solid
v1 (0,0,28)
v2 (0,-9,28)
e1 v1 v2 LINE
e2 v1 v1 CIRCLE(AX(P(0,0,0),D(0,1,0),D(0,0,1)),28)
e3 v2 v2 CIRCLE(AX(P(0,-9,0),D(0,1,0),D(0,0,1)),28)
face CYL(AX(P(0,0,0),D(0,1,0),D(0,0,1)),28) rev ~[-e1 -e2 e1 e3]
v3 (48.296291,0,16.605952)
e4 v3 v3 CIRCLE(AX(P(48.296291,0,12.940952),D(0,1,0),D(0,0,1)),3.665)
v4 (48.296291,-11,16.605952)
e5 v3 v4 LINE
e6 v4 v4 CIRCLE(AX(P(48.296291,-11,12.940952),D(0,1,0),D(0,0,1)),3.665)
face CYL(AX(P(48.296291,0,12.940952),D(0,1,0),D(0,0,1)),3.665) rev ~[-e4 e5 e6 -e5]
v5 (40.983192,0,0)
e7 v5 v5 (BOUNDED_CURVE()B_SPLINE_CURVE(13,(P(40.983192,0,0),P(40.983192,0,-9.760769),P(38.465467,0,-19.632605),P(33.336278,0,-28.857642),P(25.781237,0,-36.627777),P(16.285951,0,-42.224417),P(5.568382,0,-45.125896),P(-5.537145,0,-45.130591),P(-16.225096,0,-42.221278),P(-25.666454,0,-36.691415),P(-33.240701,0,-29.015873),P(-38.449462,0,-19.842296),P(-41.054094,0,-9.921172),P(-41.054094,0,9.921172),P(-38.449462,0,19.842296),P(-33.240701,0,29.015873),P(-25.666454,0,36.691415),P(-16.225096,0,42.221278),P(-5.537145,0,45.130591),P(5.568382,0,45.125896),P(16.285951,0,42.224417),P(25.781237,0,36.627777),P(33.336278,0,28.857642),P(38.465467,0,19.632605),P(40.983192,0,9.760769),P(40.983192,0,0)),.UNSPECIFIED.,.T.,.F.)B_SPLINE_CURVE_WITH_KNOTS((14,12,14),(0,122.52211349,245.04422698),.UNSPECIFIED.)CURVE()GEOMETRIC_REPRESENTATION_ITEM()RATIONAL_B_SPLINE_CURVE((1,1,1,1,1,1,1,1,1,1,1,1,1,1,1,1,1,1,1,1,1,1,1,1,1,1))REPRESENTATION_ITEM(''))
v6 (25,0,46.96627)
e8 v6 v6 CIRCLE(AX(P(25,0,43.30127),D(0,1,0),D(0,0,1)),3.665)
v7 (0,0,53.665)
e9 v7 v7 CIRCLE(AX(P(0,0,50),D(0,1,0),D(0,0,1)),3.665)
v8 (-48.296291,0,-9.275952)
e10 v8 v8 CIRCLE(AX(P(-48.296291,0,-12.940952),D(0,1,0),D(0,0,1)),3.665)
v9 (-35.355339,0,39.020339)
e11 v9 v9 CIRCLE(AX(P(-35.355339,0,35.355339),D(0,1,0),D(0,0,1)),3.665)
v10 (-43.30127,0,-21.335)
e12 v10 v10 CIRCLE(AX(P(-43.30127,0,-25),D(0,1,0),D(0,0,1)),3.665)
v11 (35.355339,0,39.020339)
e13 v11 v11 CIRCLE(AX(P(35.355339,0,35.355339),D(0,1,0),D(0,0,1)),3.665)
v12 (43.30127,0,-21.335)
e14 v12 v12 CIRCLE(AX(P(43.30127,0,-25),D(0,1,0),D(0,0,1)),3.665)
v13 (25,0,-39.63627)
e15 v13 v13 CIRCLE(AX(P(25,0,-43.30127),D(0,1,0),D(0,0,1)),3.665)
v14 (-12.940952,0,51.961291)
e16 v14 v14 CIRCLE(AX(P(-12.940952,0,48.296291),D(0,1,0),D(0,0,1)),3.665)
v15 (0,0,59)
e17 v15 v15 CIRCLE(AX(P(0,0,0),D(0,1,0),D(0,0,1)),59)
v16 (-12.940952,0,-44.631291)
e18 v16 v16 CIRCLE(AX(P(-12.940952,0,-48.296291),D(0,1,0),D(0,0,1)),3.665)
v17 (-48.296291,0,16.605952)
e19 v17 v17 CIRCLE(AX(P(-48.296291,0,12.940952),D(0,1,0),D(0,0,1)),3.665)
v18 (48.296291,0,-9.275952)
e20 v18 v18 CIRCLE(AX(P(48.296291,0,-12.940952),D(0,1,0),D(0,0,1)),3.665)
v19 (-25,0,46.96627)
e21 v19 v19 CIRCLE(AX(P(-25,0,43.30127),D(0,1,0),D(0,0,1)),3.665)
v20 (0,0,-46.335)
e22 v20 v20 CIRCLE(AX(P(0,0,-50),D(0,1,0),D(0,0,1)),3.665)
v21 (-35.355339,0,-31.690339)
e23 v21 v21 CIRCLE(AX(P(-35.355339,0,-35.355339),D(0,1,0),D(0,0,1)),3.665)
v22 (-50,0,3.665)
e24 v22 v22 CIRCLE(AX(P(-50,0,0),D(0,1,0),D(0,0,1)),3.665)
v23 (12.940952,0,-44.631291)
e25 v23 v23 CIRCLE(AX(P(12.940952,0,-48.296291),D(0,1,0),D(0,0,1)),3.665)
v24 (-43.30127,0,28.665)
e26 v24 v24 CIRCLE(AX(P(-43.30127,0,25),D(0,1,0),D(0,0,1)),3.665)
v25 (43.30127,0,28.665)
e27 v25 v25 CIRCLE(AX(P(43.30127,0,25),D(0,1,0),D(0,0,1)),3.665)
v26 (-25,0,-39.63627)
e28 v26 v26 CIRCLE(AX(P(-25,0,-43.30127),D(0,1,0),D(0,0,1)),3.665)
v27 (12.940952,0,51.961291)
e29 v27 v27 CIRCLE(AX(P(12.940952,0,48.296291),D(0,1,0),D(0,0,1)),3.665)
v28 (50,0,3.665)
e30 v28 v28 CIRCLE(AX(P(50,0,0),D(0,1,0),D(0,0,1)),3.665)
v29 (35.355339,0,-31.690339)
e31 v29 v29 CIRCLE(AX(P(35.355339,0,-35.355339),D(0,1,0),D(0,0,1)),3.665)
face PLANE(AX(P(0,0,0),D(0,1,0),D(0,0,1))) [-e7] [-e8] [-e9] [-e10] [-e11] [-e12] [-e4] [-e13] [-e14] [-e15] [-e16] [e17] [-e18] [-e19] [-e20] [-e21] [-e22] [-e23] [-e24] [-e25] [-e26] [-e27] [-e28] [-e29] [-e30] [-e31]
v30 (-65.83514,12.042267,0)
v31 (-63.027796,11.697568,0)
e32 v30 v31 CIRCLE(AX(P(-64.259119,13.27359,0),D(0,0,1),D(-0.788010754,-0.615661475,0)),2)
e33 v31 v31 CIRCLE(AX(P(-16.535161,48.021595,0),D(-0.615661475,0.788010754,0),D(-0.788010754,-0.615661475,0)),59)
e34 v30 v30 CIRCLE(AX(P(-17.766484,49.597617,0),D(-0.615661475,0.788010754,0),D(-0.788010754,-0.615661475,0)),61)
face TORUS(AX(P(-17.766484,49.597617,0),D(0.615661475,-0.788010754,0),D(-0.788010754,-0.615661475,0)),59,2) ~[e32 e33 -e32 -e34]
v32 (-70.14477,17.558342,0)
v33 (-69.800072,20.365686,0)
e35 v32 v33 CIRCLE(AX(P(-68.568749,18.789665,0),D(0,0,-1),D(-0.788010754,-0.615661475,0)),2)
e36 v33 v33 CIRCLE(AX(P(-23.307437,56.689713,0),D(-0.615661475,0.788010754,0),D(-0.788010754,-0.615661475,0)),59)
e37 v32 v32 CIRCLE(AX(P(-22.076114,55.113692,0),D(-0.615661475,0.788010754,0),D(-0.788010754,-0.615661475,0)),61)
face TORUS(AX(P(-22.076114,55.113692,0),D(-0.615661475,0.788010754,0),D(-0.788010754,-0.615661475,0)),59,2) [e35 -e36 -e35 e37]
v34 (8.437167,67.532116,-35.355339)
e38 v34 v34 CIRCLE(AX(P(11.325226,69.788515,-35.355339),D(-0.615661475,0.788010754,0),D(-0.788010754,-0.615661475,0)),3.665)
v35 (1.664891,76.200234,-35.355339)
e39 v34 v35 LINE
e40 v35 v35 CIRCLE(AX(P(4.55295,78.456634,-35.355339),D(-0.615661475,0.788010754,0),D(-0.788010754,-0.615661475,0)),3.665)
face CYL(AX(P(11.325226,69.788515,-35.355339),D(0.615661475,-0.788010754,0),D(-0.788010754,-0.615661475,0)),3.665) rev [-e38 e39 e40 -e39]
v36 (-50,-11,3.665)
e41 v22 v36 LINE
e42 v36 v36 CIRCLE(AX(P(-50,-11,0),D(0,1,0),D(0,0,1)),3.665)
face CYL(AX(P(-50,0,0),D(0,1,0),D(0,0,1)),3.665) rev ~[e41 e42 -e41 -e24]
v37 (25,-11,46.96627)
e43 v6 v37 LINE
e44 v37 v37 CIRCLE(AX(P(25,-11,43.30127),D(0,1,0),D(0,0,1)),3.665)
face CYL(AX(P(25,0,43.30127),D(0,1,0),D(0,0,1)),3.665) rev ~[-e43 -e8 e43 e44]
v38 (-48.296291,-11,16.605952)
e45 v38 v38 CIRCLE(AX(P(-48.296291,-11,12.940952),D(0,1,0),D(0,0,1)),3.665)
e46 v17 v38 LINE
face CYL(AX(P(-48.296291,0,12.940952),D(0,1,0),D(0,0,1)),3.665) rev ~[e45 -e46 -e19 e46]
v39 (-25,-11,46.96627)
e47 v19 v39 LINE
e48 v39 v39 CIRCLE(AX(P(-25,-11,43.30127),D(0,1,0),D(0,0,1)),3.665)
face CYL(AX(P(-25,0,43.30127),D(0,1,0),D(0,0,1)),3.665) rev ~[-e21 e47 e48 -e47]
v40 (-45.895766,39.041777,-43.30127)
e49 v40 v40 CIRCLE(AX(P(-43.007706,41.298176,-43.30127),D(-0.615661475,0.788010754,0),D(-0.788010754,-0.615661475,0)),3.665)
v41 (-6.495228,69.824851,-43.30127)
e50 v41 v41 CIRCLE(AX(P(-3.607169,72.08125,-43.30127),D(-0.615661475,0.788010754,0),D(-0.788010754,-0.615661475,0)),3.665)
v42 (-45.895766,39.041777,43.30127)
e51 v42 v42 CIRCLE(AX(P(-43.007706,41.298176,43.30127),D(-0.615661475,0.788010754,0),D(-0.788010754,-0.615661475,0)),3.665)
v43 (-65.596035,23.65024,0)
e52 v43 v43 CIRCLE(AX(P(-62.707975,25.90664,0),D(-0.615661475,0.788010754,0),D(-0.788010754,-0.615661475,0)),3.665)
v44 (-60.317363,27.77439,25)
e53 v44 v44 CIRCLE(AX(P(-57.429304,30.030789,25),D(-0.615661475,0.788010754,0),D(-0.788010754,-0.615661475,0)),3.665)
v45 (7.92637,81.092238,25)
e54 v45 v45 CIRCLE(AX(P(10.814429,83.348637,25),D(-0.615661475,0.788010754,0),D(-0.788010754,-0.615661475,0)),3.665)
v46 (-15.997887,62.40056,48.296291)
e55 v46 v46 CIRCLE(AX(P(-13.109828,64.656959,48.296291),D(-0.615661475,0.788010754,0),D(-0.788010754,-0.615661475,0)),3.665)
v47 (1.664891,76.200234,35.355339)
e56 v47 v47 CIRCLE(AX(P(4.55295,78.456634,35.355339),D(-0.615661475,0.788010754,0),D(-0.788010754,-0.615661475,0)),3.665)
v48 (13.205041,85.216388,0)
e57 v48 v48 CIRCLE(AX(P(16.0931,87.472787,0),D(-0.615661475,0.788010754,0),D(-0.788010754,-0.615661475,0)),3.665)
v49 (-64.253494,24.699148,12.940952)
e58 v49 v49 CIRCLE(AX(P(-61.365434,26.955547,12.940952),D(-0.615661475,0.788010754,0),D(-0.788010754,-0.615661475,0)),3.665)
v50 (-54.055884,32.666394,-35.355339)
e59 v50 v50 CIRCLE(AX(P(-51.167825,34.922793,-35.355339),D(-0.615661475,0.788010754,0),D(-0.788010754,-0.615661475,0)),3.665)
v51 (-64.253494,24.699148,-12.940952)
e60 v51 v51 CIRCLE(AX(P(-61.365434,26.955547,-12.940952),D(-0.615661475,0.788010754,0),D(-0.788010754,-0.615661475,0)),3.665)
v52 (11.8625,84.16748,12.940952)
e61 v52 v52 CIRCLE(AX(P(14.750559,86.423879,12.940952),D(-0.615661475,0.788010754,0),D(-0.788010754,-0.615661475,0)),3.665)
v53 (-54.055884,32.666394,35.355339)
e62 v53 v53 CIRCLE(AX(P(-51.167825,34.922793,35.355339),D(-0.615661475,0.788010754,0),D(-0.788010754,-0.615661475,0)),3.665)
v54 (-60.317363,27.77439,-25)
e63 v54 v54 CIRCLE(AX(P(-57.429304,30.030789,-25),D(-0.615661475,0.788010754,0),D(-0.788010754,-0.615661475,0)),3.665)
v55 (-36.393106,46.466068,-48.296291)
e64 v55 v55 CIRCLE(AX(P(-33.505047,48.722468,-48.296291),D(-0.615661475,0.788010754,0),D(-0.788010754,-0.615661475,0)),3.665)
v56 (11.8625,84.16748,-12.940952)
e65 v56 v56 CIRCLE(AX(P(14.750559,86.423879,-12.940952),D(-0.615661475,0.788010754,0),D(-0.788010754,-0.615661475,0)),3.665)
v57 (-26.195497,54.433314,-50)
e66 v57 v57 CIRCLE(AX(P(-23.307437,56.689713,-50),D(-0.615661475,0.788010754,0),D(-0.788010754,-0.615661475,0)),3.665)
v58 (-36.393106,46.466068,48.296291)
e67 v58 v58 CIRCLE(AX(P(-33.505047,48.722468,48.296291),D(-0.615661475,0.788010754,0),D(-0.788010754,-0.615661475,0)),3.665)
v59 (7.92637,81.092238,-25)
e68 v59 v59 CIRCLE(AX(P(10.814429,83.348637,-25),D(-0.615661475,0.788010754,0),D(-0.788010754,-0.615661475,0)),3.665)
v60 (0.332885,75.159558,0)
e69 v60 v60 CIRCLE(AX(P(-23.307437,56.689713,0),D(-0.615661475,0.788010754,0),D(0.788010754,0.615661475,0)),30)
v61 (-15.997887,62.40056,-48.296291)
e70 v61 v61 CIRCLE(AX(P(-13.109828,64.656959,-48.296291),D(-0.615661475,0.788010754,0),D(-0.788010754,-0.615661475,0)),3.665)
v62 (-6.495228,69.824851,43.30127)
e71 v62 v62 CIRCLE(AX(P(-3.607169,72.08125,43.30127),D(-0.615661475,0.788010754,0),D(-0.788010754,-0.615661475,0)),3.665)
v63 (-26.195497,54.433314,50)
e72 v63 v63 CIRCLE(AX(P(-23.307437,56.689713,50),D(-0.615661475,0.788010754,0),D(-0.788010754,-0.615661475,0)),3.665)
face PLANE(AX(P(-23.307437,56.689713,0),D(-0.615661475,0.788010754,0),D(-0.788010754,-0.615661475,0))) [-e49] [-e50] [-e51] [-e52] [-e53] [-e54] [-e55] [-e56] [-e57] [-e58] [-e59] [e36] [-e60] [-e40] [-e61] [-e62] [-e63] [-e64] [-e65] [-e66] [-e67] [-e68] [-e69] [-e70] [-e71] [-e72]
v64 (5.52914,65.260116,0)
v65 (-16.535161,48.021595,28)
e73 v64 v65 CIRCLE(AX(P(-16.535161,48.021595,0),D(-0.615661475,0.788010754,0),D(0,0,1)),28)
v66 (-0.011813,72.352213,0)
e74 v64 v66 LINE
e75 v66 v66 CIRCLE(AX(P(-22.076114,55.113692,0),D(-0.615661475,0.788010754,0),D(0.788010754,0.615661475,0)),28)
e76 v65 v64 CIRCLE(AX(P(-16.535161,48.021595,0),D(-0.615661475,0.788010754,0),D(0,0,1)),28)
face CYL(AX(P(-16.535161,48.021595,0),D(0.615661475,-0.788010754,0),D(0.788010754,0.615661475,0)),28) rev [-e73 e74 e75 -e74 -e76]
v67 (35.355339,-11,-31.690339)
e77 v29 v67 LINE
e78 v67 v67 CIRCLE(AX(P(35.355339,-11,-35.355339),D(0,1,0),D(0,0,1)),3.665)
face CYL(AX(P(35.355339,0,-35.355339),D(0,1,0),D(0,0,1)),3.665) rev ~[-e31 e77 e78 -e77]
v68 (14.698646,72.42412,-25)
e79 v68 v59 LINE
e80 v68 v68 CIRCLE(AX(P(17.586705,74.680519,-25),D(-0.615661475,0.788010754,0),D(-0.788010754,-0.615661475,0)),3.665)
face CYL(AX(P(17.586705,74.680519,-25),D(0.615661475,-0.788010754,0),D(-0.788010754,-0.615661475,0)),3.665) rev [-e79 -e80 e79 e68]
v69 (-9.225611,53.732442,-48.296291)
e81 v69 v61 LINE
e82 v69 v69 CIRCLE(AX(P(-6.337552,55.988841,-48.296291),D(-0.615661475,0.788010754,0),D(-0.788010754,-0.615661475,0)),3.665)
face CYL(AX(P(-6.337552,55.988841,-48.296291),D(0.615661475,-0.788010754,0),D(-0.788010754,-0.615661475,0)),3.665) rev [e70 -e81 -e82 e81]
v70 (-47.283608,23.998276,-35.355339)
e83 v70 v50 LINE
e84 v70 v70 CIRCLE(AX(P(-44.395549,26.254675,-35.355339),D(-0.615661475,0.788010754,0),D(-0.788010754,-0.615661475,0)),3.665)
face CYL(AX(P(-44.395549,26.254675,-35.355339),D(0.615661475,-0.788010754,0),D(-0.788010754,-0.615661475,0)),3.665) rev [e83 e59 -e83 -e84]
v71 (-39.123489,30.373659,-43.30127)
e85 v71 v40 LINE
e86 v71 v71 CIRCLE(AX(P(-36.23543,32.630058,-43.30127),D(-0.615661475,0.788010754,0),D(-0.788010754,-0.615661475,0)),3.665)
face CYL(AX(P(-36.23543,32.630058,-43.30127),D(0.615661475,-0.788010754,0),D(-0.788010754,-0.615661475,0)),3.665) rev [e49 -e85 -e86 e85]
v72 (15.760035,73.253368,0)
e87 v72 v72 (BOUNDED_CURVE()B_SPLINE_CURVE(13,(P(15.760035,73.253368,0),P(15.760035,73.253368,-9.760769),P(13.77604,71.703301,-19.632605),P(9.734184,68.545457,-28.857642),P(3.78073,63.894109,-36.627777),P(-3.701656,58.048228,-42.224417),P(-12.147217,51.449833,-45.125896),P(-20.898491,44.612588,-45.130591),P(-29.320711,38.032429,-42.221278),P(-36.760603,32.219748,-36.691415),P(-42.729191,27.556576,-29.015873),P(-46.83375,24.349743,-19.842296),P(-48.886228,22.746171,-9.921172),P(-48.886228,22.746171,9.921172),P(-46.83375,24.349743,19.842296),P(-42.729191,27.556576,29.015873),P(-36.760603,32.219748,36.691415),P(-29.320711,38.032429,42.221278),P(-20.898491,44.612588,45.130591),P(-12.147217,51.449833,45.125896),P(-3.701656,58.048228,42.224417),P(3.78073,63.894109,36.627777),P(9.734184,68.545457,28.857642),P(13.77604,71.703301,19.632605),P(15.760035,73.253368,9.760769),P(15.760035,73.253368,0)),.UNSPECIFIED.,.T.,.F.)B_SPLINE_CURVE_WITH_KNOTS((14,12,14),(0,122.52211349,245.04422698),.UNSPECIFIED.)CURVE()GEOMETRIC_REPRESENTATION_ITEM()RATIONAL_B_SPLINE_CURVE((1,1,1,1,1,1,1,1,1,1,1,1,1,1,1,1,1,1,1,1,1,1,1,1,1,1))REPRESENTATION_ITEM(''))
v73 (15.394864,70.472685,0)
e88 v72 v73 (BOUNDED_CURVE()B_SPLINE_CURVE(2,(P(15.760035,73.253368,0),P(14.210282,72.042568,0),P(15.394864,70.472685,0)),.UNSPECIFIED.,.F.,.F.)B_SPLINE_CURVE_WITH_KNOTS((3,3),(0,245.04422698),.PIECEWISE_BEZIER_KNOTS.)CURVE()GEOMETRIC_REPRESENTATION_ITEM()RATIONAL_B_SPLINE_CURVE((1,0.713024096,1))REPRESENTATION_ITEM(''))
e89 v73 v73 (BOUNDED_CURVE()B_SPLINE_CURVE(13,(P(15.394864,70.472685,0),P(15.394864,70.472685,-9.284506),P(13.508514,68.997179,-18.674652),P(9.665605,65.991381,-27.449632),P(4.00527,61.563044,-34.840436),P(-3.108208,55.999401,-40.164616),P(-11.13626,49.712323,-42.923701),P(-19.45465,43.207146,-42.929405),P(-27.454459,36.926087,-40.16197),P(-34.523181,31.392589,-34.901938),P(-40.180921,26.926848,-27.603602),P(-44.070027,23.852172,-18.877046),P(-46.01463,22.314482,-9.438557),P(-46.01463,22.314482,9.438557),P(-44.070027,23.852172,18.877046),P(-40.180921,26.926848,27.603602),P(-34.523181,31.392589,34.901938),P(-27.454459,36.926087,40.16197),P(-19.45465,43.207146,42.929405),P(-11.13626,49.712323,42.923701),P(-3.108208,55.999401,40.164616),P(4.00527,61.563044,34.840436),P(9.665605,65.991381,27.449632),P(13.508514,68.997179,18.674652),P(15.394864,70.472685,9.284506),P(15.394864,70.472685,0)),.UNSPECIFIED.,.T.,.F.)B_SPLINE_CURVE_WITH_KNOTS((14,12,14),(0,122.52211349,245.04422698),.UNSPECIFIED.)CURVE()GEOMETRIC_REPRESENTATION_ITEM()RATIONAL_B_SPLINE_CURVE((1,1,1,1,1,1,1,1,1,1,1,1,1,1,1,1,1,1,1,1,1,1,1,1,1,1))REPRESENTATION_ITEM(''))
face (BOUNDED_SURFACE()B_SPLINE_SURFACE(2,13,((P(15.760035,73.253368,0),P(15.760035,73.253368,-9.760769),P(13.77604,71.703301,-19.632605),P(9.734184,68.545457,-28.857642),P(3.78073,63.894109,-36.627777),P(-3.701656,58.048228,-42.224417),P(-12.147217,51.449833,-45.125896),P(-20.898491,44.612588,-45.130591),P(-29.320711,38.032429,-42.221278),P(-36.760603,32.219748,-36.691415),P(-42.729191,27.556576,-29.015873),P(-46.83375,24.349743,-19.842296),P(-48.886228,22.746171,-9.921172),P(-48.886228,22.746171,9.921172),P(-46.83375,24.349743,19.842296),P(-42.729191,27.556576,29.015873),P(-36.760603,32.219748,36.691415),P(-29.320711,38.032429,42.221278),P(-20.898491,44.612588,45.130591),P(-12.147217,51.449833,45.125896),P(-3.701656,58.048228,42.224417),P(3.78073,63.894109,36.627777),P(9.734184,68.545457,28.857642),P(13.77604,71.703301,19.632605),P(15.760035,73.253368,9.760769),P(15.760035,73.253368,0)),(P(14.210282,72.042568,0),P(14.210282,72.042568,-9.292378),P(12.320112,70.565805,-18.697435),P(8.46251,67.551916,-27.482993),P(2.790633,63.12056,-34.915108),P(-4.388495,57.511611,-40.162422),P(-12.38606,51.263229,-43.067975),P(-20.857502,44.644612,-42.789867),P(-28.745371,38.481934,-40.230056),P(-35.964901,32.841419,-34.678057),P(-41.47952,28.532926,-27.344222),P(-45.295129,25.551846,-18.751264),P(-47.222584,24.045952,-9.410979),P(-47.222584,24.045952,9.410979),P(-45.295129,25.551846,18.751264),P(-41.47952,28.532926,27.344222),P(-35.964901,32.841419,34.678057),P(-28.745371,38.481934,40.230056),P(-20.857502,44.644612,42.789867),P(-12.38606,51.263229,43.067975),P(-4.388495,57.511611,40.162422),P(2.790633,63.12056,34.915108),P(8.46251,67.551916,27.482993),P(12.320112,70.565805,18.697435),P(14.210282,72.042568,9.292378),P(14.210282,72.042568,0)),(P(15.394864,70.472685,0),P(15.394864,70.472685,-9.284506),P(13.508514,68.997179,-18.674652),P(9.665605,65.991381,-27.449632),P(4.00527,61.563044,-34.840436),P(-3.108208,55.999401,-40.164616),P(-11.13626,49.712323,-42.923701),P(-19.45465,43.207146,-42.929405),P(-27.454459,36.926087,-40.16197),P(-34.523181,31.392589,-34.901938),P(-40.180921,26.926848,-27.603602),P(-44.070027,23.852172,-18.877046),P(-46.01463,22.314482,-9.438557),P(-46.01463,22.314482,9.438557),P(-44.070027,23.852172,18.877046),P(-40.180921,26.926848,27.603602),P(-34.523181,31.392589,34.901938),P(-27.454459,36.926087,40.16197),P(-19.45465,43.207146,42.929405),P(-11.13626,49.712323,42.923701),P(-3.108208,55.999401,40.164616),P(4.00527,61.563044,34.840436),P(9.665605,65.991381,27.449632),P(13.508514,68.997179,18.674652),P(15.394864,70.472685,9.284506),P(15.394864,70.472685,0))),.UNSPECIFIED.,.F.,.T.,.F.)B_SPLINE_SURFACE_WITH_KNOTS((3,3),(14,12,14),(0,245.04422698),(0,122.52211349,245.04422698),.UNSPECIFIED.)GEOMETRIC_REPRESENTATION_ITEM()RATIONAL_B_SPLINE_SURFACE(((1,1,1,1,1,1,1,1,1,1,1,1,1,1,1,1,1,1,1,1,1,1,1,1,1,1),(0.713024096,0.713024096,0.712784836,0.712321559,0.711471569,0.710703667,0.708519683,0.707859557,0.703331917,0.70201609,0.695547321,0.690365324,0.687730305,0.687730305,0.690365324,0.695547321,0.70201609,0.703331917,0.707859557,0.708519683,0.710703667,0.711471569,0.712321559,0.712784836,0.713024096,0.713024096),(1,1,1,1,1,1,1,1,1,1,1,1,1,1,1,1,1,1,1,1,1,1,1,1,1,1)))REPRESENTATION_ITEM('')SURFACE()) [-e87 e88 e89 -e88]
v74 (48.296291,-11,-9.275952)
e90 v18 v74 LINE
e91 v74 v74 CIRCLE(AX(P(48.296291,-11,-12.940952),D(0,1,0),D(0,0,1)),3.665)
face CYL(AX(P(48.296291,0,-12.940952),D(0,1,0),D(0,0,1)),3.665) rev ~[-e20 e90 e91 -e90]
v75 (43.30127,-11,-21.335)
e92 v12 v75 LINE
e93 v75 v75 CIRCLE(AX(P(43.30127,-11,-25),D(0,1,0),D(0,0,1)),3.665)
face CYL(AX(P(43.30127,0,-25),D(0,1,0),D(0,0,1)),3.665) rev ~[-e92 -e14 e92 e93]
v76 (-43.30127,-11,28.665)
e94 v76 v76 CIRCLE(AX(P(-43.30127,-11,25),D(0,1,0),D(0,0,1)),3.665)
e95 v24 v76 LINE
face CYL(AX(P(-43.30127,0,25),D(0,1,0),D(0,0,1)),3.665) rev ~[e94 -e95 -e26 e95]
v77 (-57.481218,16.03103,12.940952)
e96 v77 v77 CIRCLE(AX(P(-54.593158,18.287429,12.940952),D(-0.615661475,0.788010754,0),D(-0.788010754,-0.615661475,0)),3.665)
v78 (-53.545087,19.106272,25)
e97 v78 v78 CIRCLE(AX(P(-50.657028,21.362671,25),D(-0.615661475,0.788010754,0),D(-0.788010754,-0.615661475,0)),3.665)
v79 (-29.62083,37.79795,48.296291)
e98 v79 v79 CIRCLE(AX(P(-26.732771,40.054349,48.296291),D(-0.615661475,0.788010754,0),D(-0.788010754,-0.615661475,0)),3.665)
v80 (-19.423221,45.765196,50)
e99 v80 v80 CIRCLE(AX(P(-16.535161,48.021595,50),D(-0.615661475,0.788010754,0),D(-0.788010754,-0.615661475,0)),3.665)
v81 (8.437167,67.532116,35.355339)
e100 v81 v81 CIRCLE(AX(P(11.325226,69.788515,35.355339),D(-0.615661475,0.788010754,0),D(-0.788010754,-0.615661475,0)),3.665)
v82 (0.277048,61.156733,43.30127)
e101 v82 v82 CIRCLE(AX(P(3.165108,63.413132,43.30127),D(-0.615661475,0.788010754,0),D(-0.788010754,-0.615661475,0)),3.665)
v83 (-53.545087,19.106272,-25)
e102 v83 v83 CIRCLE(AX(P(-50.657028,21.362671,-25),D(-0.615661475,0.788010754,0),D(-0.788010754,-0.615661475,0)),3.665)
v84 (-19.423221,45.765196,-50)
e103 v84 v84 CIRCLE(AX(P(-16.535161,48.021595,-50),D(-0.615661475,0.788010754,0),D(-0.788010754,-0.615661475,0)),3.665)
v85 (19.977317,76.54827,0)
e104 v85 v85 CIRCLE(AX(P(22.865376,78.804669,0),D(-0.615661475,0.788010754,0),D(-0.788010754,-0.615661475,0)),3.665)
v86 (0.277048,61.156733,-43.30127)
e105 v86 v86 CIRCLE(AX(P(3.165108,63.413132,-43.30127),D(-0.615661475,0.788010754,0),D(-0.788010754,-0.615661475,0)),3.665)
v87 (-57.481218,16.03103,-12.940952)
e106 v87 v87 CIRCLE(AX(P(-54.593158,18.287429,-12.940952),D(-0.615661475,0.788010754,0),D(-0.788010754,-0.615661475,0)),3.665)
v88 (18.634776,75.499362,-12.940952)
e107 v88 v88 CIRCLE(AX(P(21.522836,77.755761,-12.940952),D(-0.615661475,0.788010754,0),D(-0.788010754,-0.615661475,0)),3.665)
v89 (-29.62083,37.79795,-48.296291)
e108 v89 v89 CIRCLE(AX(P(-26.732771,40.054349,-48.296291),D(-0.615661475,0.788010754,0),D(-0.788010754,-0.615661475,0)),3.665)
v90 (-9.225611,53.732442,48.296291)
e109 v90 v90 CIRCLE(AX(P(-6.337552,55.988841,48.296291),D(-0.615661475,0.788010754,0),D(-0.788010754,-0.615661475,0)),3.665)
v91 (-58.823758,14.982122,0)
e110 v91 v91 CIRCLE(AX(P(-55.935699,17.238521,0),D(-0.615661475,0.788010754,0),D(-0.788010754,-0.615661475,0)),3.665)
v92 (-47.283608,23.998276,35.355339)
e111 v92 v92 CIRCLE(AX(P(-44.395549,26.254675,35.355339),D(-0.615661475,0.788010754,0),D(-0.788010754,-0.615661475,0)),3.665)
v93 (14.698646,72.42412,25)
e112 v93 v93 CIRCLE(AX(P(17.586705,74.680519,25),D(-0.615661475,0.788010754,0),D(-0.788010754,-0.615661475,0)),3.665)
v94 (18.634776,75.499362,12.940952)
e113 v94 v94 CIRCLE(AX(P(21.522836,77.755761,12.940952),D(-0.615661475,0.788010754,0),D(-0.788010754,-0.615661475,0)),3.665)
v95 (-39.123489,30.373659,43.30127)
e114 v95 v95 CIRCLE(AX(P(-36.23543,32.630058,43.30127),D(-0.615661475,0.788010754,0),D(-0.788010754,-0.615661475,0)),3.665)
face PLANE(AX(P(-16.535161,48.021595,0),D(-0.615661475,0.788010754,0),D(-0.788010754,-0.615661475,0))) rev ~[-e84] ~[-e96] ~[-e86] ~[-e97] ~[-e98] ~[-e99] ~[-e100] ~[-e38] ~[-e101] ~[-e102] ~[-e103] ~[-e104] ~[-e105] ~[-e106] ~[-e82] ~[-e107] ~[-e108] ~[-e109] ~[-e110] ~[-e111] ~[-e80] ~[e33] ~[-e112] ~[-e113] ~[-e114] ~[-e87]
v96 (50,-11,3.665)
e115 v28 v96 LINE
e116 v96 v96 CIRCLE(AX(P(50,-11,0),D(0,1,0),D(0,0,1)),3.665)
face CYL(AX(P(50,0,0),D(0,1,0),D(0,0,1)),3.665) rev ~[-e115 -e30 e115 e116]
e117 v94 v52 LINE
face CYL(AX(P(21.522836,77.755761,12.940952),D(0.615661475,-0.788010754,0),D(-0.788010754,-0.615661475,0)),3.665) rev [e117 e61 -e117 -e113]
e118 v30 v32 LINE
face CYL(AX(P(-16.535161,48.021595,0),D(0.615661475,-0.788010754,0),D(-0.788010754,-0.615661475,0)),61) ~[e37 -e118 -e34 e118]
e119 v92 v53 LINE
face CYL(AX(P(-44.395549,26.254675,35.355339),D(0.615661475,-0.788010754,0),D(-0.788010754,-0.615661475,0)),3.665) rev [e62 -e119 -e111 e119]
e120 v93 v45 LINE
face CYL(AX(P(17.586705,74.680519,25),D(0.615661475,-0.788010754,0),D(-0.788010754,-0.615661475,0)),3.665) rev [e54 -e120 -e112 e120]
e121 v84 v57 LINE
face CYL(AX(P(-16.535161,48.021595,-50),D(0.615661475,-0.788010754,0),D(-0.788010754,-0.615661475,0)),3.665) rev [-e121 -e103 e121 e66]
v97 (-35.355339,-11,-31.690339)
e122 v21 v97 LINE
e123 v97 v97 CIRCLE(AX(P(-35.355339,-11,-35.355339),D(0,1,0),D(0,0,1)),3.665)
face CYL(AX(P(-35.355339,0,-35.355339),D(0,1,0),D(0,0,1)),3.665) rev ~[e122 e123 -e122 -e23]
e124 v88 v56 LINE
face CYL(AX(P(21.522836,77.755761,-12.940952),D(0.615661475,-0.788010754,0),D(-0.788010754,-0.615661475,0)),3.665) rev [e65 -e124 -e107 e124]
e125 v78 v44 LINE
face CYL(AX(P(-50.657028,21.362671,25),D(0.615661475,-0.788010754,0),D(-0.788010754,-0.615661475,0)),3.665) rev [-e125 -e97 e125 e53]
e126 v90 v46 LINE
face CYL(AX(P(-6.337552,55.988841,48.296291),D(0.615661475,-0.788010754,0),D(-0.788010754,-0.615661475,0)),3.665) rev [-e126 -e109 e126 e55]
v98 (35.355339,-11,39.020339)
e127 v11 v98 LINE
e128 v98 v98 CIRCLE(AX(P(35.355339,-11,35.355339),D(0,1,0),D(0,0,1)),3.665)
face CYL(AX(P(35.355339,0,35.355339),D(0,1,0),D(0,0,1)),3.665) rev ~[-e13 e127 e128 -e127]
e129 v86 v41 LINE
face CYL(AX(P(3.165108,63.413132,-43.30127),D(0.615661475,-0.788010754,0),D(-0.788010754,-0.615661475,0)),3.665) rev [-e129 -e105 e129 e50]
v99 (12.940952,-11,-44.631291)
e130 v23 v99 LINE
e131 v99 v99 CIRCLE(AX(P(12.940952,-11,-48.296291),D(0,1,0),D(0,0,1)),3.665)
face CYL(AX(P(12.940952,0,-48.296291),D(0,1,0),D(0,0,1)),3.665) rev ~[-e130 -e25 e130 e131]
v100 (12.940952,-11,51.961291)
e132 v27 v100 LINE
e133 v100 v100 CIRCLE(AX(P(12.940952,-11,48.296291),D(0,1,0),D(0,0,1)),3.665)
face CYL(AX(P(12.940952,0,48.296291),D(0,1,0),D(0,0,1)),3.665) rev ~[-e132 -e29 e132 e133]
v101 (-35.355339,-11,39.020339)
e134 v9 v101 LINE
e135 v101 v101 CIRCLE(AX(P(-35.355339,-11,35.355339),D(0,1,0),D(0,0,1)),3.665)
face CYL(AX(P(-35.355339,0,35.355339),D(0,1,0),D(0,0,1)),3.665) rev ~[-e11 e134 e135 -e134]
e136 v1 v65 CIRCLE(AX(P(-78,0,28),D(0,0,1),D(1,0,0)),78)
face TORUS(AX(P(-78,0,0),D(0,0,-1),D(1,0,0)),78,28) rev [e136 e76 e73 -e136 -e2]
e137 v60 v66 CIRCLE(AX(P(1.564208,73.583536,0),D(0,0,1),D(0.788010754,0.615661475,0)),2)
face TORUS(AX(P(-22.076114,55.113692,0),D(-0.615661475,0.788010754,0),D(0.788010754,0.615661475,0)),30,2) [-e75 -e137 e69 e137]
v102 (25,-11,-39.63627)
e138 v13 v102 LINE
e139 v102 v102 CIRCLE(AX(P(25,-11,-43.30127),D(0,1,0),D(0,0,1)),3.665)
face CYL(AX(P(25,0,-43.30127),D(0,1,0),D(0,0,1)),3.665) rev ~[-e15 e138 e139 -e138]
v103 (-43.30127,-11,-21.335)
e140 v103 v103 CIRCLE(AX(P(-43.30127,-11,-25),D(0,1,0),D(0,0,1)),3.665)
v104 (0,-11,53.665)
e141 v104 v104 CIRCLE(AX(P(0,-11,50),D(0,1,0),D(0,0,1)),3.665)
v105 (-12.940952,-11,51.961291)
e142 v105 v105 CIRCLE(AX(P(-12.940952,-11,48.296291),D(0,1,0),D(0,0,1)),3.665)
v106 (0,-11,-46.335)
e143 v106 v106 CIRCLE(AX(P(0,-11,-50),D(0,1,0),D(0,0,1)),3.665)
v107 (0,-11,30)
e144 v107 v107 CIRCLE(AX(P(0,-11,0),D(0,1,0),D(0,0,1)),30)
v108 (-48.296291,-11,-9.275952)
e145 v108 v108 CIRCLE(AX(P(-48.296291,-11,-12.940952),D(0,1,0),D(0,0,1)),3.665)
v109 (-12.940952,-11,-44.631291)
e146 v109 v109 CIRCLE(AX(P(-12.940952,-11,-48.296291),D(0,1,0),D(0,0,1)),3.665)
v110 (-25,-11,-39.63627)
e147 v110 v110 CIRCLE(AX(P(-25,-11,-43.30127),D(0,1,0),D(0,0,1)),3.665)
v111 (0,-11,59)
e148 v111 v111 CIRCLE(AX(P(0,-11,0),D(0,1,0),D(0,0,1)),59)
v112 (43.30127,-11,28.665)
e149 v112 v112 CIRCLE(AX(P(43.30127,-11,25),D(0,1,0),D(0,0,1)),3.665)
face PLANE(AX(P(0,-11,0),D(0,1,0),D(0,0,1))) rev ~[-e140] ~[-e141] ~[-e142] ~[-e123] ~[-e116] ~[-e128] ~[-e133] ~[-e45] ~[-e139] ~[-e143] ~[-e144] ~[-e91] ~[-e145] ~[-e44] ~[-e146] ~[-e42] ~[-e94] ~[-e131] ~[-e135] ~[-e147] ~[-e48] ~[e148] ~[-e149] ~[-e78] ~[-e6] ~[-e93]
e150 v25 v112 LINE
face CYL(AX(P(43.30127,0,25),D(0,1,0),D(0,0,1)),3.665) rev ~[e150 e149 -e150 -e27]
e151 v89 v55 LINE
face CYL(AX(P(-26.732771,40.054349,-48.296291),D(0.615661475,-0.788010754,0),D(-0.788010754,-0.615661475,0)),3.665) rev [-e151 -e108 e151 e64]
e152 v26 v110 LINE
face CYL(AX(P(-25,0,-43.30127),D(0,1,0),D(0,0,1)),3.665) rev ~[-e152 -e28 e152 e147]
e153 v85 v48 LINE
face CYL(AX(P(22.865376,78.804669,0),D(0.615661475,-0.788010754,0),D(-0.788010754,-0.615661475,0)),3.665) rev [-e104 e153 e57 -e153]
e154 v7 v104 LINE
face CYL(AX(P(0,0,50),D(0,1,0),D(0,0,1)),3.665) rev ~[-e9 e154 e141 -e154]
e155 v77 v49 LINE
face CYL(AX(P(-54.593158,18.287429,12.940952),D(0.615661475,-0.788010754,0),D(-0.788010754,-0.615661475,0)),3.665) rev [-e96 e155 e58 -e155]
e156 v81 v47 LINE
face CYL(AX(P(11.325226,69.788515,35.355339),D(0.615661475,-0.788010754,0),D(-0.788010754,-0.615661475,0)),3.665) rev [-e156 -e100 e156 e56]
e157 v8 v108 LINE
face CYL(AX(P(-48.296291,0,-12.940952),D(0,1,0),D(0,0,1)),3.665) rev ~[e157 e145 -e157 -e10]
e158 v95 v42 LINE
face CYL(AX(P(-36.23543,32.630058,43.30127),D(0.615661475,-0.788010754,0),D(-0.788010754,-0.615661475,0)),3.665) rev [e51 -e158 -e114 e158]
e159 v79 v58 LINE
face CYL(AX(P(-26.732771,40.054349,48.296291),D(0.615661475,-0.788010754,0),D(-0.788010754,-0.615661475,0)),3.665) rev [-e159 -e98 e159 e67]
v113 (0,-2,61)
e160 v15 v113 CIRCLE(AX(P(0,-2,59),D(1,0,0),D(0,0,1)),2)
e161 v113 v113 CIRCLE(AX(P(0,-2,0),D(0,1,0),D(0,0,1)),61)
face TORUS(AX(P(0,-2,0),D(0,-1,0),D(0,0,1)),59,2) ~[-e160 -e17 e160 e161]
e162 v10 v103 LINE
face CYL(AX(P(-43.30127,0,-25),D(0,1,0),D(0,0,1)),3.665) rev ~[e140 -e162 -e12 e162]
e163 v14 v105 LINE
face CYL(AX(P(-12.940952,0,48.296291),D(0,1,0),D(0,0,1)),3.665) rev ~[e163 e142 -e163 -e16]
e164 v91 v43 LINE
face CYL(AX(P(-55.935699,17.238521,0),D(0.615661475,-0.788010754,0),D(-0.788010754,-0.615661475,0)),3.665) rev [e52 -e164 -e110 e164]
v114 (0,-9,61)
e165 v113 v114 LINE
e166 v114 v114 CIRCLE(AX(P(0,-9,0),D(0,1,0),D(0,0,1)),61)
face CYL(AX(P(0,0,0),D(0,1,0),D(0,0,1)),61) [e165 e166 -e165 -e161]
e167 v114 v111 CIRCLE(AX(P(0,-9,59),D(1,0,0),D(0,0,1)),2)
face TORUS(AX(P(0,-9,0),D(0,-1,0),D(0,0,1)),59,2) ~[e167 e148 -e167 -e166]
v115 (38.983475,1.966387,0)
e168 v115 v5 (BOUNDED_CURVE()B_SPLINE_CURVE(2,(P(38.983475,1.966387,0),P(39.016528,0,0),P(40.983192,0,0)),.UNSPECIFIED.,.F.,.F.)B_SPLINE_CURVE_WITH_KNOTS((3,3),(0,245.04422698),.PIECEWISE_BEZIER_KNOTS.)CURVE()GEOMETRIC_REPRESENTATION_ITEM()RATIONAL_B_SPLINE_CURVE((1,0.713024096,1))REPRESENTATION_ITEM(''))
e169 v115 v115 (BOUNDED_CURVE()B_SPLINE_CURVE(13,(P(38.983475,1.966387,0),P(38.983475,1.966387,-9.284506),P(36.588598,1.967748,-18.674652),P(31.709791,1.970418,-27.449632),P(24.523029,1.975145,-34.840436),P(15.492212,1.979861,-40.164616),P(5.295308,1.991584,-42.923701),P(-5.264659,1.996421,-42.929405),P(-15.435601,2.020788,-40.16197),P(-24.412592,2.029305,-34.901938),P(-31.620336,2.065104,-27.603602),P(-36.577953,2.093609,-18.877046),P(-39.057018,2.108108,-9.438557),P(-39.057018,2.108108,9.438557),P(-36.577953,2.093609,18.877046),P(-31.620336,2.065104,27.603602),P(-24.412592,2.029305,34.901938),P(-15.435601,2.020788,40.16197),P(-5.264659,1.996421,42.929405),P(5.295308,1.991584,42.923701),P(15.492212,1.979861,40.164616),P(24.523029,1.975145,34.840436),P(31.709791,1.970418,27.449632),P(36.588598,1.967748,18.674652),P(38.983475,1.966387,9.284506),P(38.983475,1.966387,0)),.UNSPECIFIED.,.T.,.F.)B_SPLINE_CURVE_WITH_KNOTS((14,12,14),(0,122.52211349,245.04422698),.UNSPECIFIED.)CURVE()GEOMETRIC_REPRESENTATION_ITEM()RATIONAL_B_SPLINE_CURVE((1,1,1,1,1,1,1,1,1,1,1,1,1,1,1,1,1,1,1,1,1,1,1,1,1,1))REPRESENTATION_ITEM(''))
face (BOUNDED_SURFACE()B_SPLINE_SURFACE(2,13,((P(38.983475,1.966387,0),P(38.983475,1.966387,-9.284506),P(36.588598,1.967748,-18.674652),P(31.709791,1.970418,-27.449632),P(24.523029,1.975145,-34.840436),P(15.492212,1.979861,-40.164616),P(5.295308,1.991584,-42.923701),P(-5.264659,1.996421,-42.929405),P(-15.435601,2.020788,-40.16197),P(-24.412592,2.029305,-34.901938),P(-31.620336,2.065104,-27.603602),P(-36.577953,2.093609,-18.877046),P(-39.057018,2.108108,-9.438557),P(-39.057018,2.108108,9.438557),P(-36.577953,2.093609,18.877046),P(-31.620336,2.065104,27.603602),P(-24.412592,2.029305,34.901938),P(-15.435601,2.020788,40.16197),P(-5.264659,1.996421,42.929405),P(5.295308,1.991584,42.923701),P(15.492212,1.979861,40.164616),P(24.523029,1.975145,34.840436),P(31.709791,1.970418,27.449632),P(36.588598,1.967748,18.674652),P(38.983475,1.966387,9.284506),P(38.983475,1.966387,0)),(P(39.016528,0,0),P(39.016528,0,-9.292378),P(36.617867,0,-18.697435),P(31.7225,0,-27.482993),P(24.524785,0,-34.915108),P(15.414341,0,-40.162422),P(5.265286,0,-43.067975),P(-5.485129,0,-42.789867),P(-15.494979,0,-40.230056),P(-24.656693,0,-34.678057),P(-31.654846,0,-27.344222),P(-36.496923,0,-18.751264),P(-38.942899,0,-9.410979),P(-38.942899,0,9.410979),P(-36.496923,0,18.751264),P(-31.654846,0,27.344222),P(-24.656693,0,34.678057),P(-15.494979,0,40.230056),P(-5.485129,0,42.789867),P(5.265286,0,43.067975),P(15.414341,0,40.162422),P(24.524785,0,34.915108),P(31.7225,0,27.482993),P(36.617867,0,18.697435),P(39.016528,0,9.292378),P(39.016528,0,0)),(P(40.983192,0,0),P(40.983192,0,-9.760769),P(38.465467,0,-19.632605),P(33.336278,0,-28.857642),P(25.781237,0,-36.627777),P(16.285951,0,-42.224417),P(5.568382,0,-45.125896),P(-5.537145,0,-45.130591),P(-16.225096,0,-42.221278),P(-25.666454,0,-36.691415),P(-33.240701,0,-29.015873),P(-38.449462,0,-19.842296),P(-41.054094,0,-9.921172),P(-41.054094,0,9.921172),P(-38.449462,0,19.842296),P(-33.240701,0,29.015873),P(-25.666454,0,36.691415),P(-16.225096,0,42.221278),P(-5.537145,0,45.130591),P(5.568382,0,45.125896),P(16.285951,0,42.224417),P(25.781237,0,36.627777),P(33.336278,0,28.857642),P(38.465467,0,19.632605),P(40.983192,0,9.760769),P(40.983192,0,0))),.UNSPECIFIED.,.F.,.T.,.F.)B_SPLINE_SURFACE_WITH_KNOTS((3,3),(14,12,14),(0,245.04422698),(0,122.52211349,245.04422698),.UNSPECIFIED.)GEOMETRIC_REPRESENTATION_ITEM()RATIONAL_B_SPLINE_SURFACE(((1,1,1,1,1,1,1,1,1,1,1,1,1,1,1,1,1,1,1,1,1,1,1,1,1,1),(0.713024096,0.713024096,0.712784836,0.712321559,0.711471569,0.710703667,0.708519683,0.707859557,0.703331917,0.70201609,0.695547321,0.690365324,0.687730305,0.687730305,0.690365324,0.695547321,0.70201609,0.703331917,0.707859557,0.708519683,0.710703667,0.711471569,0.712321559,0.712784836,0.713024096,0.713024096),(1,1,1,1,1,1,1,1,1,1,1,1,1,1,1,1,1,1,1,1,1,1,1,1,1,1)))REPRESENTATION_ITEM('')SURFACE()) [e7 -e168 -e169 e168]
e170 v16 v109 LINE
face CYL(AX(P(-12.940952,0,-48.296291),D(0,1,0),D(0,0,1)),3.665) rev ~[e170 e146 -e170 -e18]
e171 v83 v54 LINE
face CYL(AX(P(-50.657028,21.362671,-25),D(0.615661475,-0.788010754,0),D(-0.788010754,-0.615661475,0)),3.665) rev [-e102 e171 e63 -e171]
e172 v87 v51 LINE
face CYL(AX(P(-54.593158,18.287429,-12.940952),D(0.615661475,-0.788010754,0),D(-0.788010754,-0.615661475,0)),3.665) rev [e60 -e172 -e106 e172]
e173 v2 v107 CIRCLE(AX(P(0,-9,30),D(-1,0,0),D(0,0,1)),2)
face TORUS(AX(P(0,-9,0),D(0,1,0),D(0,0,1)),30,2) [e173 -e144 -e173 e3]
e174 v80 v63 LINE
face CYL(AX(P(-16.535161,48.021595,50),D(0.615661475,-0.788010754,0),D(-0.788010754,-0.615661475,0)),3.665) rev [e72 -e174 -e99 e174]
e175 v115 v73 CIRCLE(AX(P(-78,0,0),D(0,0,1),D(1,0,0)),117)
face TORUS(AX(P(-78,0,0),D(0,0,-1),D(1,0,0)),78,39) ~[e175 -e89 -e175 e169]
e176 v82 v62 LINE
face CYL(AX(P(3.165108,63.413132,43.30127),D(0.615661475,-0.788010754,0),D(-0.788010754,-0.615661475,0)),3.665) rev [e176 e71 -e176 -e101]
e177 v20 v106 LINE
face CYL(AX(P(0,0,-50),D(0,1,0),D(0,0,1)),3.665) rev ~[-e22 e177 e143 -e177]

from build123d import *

# Parameters (mm, degrees)
BASE_FLANGE_SKETCH_R       = 61
BASE_FLANGE_SKETCH_R_2     = 28
BASE_FLANGE_SKETCH_R_3     = 3.665
BASE_FLANGE_24X_7_33_DEPTH = 11
BEND_PROFILE_SKETCH_R      = 39
BEND_PROFILE_SKETCH_R_2    = 28
PIPE_BEND_38DEG_ANGLE      = 38
END_FLANGE_SKETCH_R        = 61
END_FLANGE_SKETCH_R_2      = 28
END_FLANGE_SKETCH_R_3      = 3.665
END_FLANGE_24X_7_33_DEPTH  = 11
EDGE_FILLETS_R2_R          = 2


with BuildPart() as part:
    # Base Flange Sketch → Base Flange 24xØ7.33 (new body)
    with BuildSketch(Plane(origin=(0, 0, 0), x_dir=(1, 0, 0), z_dir=(0, 1, 0))):
        with Locations(Location((0, 0, 0), (0, 0, 270))):
            Circle(BASE_FLANGE_SKETCH_R)
        with Locations(Location((0, 0, 0), (0, 0, 270))):
            Circle(BASE_FLANGE_SKETCH_R_2, mode=Mode.SUBTRACT)
        with Locations(Location((0, 50, 0), (0, 0, 270))):
            Circle(BASE_FLANGE_SKETCH_R_3, mode=Mode.SUBTRACT)
        with Locations(Location((12.940952255, 48.296291314, 0), (0, 0, 270))):
            Circle(BASE_FLANGE_SKETCH_R_3, mode=Mode.SUBTRACT)
        with Locations(Location((25, 43.301270189, 0), (0, 0, 270))):
            Circle(BASE_FLANGE_SKETCH_R_3, mode=Mode.SUBTRACT)
        with Locations(Location((35.355339059, 35.355339059, 0), (0, 0, 270))):
            Circle(BASE_FLANGE_SKETCH_R_3, mode=Mode.SUBTRACT)
        with Locations(Location((43.301270189, 25, 0), (0, 0, 270))):
            Circle(BASE_FLANGE_SKETCH_R_3, mode=Mode.SUBTRACT)
        with Locations(Location((48.296291314, 12.940952255, 0), (0, 0, 270))):
            Circle(BASE_FLANGE_SKETCH_R_3, mode=Mode.SUBTRACT)
        with Locations(Location((50, 0, 0), (0, 0, 270))):
            Circle(BASE_FLANGE_SKETCH_R_3, mode=Mode.SUBTRACT)
        with Locations(Location((48.296291314, -12.940952255, 0), (0, 0, 270))):
            Circle(BASE_FLANGE_SKETCH_R_3, mode=Mode.SUBTRACT)
        with Locations(Location((43.301270189, -25, 0), (0, 0, 270))):
            Circle(BASE_FLANGE_SKETCH_R_3, mode=Mode.SUBTRACT)
        with Locations(Location((35.355339059, -35.355339059, 0), (0, 0, 270))):
            Circle(BASE_FLANGE_SKETCH_R_3, mode=Mode.SUBTRACT)
        with Locations(Location((25, -43.301270189, 0), (0, 0, 270))):
            Circle(BASE_FLANGE_SKETCH_R_3, mode=Mode.SUBTRACT)
        with Locations(Location((12.940952255, -48.296291314, 0), (0, 0, 270))):
            Circle(BASE_FLANGE_SKETCH_R_3, mode=Mode.SUBTRACT)
        with Locations(Location((0, -50, 0), (0, 0, 270))):
            Circle(BASE_FLANGE_SKETCH_R_3, mode=Mode.SUBTRACT)
        with Locations(Location((-12.940952255, -48.296291314, 0), (0, 0, 270))):
            Circle(BASE_FLANGE_SKETCH_R_3, mode=Mode.SUBTRACT)
        with Locations(Location((-25, -43.301270189, 0), (0, 0, 270))):
            Circle(BASE_FLANGE_SKETCH_R_3, mode=Mode.SUBTRACT)
        with Locations(Location((-35.355339059, -35.355339059, 0), (0, 0, 270))):
            Circle(BASE_FLANGE_SKETCH_R_3, mode=Mode.SUBTRACT)
        with Locations(Location((-43.301270189, -25, 0), (0, 0, 270))):
            Circle(BASE_FLANGE_SKETCH_R_3, mode=Mode.SUBTRACT)
        with Locations(Location((-48.296291314, -12.940952255, 0), (0, 0, 270))):
            Circle(BASE_FLANGE_SKETCH_R_3, mode=Mode.SUBTRACT)
        with Locations(Location((-50, 0, 0), (0, 0, 270))):
            Circle(BASE_FLANGE_SKETCH_R_3, mode=Mode.SUBTRACT)
        with Locations(Location((-48.296291314, 12.940952255, 0), (0, 0, 270))):
            Circle(BASE_FLANGE_SKETCH_R_3, mode=Mode.SUBTRACT)
        with Locations(Location((-43.301270189, 25, 0), (0, 0, 270))):
            Circle(BASE_FLANGE_SKETCH_R_3, mode=Mode.SUBTRACT)
        with Locations(Location((-35.355339059, 35.355339059, 0), (0, 0, 270))):
            Circle(BASE_FLANGE_SKETCH_R_3, mode=Mode.SUBTRACT)
        with Locations(Location((-25, 43.301270189, 0), (0, 0, 270))):
            Circle(BASE_FLANGE_SKETCH_R_3, mode=Mode.SUBTRACT)
        with Locations(Location((-12.940952255, 48.296291314, 0), (0, 0, 270))):
            Circle(BASE_FLANGE_SKETCH_R_3, mode=Mode.SUBTRACT)
    extrude(amount=-BASE_FLANGE_24X_7_33_DEPTH)

    # Bend Profile Sketch → Pipe Bend 38deg (revolve)
    with BuildSketch(Plane(origin=(0, 0, 0), x_dir=(1, 0, 0), z_dir=(0, 1, 0))):
        Circle(BEND_PROFILE_SKETCH_R)
        with Locations(Location((0, 0, 0), (0, 0, 270))):
            Circle(BEND_PROFILE_SKETCH_R_2, mode=Mode.SUBTRACT)
    revolve(axis=Axis((-78, 0, -90.684737963), (0, 0, 1)), revolution_arc=PIPE_BEND_38DEG_ANGLE)

    # End Flange Sketch → End Flange 24xØ7.33 (add)
    with BuildSketch(Plane(origin=(-29.565046072, 37.841533325, 0), x_dir=(0.7880107536067209, 0.6156614753256596, 0), z_dir=(-0.6156614753256596, 0.7880107536067209, 0))):
        with Locations(Location((16.535161219, 0, 0), (0, 0, 180))):
            Circle(END_FLANGE_SKETCH_R)
        with Locations((16.535161219, 0)):
            Circle(END_FLANGE_SKETCH_R_2, mode=Mode.SUBTRACT)
        with Locations(Location((16.535161219, 50, 0), (0, 0, 180))):
            Circle(END_FLANGE_SKETCH_R_3, mode=Mode.SUBTRACT)
        with Locations(Location((29.476113474, 48.296291314, 0), (0, 0, 180))):
            Circle(END_FLANGE_SKETCH_R_3, mode=Mode.SUBTRACT)
        with Locations(Location((41.535161219, 43.301270189, 0), (0, 0, 180))):
            Circle(END_FLANGE_SKETCH_R_3, mode=Mode.SUBTRACT)
        with Locations(Location((51.890500278, 35.355339059, 0), (0, 0, 180))):
            Circle(END_FLANGE_SKETCH_R_3, mode=Mode.SUBTRACT)
        with Locations(Location((59.836431408, 25, 0), (0, 0, 180))):
            Circle(END_FLANGE_SKETCH_R_3, mode=Mode.SUBTRACT)
        with Locations(Location((64.831452533, 12.940952255, 0), (0, 0, 180))):
            Circle(END_FLANGE_SKETCH_R_3, mode=Mode.SUBTRACT)
        with Locations(Location((66.535161219, 0, 0), (0, 0, 180))):
            Circle(END_FLANGE_SKETCH_R_3, mode=Mode.SUBTRACT)
        with Locations(Location((64.831452533, -12.940952255, 0), (0, 0, 180))):
            Circle(END_FLANGE_SKETCH_R_3, mode=Mode.SUBTRACT)
        with Locations(Location((59.836431408, -25, 0), (0, 0, 180))):
            Circle(END_FLANGE_SKETCH_R_3, mode=Mode.SUBTRACT)
        with Locations(Location((51.890500278, -35.355339059, 0), (0, 0, 180))):
            Circle(END_FLANGE_SKETCH_R_3, mode=Mode.SUBTRACT)
        with Locations(Location((41.535161219, -43.301270189, 0), (0, 0, 180))):
            Circle(END_FLANGE_SKETCH_R_3, mode=Mode.SUBTRACT)
        with Locations(Location((29.476113474, -48.296291314, 0), (0, 0, 180))):
            Circle(END_FLANGE_SKETCH_R_3, mode=Mode.SUBTRACT)
        with Locations(Location((16.535161219, -50, 0), (0, 0, 180))):
            Circle(END_FLANGE_SKETCH_R_3, mode=Mode.SUBTRACT)
        with Locations(Location((3.594208964, -48.296291314, 0), (0, 0, 180))):
            Circle(END_FLANGE_SKETCH_R_3, mode=Mode.SUBTRACT)
        with Locations(Location((-8.464838781, -43.301270189, 0), (0, 0, 180))):
            Circle(END_FLANGE_SKETCH_R_3, mode=Mode.SUBTRACT)
        with Locations(Location((-18.820177841, -35.355339059, 0), (0, 0, 180))):
            Circle(END_FLANGE_SKETCH_R_3, mode=Mode.SUBTRACT)
        with Locations(Location((-26.766108971, -25, 0), (0, 0, 180))):
            Circle(END_FLANGE_SKETCH_R_3, mode=Mode.SUBTRACT)
        with Locations(Location((-31.761130096, -12.940952255, 0), (0, 0, 180))):
            Circle(END_FLANGE_SKETCH_R_3, mode=Mode.SUBTRACT)
        with Locations(Location((-33.464838781, 0, 0), (0, 0, 180))):
            Circle(END_FLANGE_SKETCH_R_3, mode=Mode.SUBTRACT)
        with Locations(Location((-31.761130096, 12.940952255, 0), (0, 0, 180))):
            Circle(END_FLANGE_SKETCH_R_3, mode=Mode.SUBTRACT)
        with Locations(Location((-26.766108971, 25, 0), (0, 0, 180))):
            Circle(END_FLANGE_SKETCH_R_3, mode=Mode.SUBTRACT)
        with Locations(Location((-18.820177841, 35.355339059, 0), (0, 0, 180))):
            Circle(END_FLANGE_SKETCH_R_3, mode=Mode.SUBTRACT)
        with Locations(Location((-8.464838781, 43.301270189, 0), (0, 0, 180))):
            Circle(END_FLANGE_SKETCH_R_3, mode=Mode.SUBTRACT)
        with Locations(Location((3.594208964, 48.296291314, 0), (0, 0, 180))):
            Circle(END_FLANGE_SKETCH_R_3, mode=Mode.SUBTRACT)
    extrude(amount=END_FLANGE_24X_7_33_DEPTH)

    # Edge Fillets R2
    edge_fillets_r2_edges = [part.edges().sort_by_distance(p)[0] for p in [
        (-39, 0, 0),
        (-47.267580609, 24.010797538, 0),
        (24.761218523, 94.24506336, 0),
        (31.533494751, 85.57694507, 0),
        (-45.371738548, 39.451192056, 0),
        (0, 0, -61),
        (0, -11, -61),
        (0, -11, -28),
    ]]
    fillet(edge_fillets_r2_edges, radius=EDGE_FILLETS_R2_R)


solid = part.part
